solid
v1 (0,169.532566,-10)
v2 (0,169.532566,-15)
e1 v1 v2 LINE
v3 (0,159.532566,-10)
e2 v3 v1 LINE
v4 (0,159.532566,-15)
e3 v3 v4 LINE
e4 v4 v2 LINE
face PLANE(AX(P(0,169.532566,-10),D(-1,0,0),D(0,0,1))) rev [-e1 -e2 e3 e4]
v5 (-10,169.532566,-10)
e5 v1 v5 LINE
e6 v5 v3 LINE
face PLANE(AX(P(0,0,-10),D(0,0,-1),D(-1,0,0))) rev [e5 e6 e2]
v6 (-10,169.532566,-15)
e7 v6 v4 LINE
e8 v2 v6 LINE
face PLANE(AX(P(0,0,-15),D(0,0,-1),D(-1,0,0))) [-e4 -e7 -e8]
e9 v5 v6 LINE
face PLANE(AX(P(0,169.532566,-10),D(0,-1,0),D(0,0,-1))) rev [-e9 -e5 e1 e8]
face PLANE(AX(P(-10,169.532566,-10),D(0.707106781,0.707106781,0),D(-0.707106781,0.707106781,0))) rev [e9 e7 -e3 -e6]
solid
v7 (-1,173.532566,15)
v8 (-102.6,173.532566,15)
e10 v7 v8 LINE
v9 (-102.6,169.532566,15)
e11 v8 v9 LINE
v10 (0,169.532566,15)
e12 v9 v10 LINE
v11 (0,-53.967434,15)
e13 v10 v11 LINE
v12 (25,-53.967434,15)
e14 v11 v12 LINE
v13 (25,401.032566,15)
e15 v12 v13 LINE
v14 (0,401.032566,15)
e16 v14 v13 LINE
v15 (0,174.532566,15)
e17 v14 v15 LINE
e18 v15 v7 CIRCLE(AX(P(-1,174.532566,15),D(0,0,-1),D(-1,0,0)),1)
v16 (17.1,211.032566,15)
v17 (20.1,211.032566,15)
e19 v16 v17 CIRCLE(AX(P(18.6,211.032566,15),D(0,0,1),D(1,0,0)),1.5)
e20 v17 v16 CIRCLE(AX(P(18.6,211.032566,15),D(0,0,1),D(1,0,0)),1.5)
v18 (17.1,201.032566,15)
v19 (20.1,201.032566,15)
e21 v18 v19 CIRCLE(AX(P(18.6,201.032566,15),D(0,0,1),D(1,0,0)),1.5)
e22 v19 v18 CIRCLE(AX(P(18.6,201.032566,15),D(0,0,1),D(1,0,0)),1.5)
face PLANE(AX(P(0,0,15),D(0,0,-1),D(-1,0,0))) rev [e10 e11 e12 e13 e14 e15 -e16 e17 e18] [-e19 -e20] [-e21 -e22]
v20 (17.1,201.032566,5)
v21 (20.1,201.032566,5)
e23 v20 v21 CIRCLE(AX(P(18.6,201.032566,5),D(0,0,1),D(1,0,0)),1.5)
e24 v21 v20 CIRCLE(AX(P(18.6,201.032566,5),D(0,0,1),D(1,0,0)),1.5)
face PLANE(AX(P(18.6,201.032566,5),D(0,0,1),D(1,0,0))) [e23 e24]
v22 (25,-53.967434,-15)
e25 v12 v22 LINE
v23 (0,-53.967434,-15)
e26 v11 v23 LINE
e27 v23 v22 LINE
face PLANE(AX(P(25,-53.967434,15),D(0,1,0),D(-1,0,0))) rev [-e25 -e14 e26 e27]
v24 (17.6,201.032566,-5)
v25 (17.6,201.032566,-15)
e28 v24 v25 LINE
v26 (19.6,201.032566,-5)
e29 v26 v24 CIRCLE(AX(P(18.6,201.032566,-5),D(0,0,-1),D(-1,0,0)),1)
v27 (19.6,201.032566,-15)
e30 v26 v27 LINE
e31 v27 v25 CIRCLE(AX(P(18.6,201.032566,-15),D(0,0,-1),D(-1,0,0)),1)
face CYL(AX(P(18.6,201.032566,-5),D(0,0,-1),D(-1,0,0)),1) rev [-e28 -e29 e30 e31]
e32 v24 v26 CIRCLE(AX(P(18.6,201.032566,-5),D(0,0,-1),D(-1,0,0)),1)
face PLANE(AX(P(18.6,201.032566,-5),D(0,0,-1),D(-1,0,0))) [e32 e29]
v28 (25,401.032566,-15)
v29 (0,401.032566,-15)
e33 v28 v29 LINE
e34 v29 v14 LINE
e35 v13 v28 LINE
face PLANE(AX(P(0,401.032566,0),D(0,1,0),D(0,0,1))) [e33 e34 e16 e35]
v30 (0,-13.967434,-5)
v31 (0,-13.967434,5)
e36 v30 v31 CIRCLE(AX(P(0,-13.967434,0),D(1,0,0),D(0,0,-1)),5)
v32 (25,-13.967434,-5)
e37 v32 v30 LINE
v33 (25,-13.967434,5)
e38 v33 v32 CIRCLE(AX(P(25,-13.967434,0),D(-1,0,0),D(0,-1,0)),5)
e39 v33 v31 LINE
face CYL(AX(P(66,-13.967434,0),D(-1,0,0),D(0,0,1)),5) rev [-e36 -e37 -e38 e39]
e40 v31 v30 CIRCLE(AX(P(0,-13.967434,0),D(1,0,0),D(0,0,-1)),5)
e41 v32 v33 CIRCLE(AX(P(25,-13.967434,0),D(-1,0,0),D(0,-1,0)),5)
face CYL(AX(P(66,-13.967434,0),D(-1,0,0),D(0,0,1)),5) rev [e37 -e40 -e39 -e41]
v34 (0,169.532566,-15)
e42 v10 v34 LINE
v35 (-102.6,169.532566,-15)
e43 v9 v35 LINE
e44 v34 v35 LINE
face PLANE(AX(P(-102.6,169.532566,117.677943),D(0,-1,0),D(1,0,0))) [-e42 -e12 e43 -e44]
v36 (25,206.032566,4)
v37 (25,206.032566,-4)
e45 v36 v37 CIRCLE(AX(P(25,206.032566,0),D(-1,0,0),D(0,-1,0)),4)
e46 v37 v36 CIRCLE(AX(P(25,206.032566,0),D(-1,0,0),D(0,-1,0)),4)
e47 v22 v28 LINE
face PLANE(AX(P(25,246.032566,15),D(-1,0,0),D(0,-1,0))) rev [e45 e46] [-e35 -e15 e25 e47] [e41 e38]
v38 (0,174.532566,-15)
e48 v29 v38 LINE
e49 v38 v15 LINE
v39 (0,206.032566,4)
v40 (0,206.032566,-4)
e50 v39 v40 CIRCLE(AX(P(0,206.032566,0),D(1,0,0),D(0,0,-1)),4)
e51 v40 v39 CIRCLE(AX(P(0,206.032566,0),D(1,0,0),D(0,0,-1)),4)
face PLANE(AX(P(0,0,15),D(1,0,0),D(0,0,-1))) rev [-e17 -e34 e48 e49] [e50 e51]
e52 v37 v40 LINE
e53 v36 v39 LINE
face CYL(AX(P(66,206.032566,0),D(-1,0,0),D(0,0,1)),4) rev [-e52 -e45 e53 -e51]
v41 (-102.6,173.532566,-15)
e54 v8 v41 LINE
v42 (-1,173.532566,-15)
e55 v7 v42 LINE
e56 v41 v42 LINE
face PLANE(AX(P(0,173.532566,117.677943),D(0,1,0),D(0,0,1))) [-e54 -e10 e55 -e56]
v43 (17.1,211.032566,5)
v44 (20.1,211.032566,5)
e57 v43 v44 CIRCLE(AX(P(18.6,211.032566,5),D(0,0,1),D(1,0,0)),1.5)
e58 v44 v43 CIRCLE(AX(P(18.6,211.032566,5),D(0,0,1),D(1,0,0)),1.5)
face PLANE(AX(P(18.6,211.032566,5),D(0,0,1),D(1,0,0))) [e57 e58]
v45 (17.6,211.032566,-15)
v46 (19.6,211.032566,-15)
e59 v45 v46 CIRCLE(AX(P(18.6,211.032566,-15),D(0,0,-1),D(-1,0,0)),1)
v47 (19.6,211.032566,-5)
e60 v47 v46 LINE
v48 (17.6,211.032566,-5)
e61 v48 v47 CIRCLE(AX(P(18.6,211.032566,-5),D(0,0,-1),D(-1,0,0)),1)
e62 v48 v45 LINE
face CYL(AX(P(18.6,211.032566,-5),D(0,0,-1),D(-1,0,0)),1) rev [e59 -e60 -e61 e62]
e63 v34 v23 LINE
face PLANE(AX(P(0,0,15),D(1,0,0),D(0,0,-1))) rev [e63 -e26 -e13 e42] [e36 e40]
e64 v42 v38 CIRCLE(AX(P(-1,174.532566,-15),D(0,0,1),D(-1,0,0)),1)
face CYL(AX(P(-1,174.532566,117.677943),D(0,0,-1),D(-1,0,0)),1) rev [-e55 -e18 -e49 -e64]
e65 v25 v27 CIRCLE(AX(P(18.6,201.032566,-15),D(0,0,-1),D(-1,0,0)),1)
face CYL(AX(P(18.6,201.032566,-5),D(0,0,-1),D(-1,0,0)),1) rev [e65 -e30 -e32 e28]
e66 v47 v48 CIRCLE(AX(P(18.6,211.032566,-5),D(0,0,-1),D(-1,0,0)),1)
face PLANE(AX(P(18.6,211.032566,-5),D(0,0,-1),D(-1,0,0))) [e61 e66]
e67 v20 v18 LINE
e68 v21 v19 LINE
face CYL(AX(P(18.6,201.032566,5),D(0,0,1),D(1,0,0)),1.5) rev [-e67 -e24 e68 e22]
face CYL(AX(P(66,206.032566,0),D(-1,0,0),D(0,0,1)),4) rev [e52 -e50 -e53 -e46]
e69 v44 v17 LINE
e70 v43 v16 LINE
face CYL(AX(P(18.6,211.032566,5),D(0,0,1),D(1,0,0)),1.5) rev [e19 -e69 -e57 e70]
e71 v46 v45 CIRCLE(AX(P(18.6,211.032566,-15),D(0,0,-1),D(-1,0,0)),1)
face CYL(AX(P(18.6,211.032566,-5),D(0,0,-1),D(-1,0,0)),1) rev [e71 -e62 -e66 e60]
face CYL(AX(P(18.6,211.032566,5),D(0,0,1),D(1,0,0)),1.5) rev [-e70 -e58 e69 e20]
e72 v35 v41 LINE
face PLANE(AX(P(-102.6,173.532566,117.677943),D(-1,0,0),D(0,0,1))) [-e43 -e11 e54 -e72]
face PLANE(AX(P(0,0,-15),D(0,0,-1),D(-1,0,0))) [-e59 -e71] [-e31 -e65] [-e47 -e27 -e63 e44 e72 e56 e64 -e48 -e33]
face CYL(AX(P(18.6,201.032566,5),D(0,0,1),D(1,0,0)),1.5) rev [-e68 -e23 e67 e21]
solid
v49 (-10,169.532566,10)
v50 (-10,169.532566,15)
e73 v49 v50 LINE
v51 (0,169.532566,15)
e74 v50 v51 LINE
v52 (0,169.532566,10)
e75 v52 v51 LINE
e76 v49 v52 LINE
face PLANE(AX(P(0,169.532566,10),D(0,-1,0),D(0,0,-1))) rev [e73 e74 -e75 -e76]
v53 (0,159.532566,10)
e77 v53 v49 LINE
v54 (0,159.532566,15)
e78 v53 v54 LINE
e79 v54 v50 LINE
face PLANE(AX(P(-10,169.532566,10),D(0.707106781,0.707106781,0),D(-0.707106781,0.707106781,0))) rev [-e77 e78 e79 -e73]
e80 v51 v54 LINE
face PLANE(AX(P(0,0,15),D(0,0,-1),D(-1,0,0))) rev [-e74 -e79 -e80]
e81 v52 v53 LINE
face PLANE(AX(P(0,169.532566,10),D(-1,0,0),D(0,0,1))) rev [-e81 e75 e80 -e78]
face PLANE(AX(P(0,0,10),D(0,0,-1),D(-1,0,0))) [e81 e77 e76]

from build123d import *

# Parameters (mm, degrees)
EXTRUDE_2_DEPTH     = 15
SKETCH_2_R          = 5
SKETCH_2_R_2        = 4
CUT_EXTRUDE_1_DEPTH = 66
SKETCH_3_W          = 102.6
SKETCH_3_H          = 4
EXTRUDE_3_DEPTH     = 30
SKETCH_4_W          = 25
SKETCH_4_H          = 30
EXTRUDE_4_DEPTH     = 155
SKETCH_5_R          = 1
CUT_EXTRUDE_2_DEPTH = 10
SKETCH_6_R          = 1.5
CUT_EXTRUDE_3_DEPTH = 10
GUSSET_1_THICKNESS  = 5
GUSSET_2_THICKNESS  = 5
FILLET_1_R          = 1


with BuildPart() as part:
    # 草图1 → 凸台-拉伸2 (new, symmetric)
    with BuildSketch(Plane.XY):
        Polygon((0, 0), (0, 246.032566337), (25, 246.032566337), (25, -38.967433663), (25, -53.967433663), (0, -53.967433663), align=None)
    extrude(amount=EXTRUDE_2_DEPTH, both=True)

    # 草图2 → 切除-拉伸1 (cut, symmetric)
    with BuildSketch(Plane.ZY):
        with Locations(Location((0, -13.967433663, 0), (0, 0, 270))):
            Circle(SKETCH_2_R)
        with Locations(Location((0, 206.032566337, 0), (0, 0, 270))):
            Circle(SKETCH_2_R_2)
    extrude(amount=CUT_EXTRUDE_1_DEPTH, both=True, mode=Mode.SUBTRACT)

    # 草图3 → 凸台-拉伸3 (add)
    with BuildSketch(Plane(origin=(0, 0, -15), x_dir=(-1, 0, 0), z_dir=(0, 0, -1))):
        with Locations((51.3, 171.532566337)):
            Rectangle(SKETCH_3_W, SKETCH_3_H)
    extrude(amount=-EXTRUDE_3_DEPTH)

    # 草图4 → 凸台-拉伸4 (add)
    with BuildSketch(Plane(origin=(0, 246.032566337, 0), x_dir=(1, 0, 0), z_dir=(0, 1, 0))):
        with Locations((12.5, 0)):
            Rectangle(SKETCH_4_W, SKETCH_4_H)
    extrude(amount=EXTRUDE_4_DEPTH)

    # 草图5 → 切除-拉伸2 (cut)
    with BuildSketch(Plane(origin=(0, 0, -15), x_dir=(-1, 0, 0), z_dir=(0, 0, -1))):
        with Locations((-18.6, 201.032566337)):
            Circle(SKETCH_5_R)
        with Locations((-18.6, 211.032566337)):
            Circle(SKETCH_5_R)
    extrude(amount=-CUT_EXTRUDE_2_DEPTH, mode=Mode.SUBTRACT)

    # 草图6 → 切除-拉伸3 (cut)
    with BuildSketch(Plane.XY.offset(15)):
        with Locations((18.6, 201.032566337)):
            Circle(SKETCH_6_R)
        with Locations((18.6, 211.032566337)):
            Circle(SKETCH_6_R)
    extrude(amount=-CUT_EXTRUDE_3_DEPTH, mode=Mode.SUBTRACT)

    # 圆角1
    fillet_1_edges = [part.edges().sort_by_distance(p)[0] for p in [
        (0, 173.532566337, 0),
    ]]
    fillet(fillet_1_edges, radius=FILLET_1_R)


with BuildPart() as body_2:
    # Gusset 1: a gusset: a plate 5.0 thick in the corner of two members, its outline drawn in place
    gusset_1_outline = Wire([Line((0, 169.532566337, -10), (-10, 169.532566337, -10)), Line((-10, 169.532566337, -10), (0, 159.532566337, -10)), Line((0, 159.532566337, -10), (0, 169.532566337, -10))])
    add(extrude(Face(gusset_1_outline), amount=GUSSET_1_THICKNESS, dir=(0, 0, -1)))


with BuildPart() as body_3:
    # Gusset 2: a gusset: a plate 5.0 thick in the corner of two members, its outline drawn in place
    gusset_2_outline = Wire([Line((0, 169.532566337, 15), (-10, 169.532566337, 15)), Line((-10, 169.532566337, 15), (0, 159.532566337, 15)), Line((0, 159.532566337, 15), (0, 169.532566337, 15))])
    add(extrude(Face(gusset_2_outline), amount=GUSSET_2_THICKNESS, dir=(0, 0, -1)))


solid = Compound([part.part, body_2.part, body_3.part])
